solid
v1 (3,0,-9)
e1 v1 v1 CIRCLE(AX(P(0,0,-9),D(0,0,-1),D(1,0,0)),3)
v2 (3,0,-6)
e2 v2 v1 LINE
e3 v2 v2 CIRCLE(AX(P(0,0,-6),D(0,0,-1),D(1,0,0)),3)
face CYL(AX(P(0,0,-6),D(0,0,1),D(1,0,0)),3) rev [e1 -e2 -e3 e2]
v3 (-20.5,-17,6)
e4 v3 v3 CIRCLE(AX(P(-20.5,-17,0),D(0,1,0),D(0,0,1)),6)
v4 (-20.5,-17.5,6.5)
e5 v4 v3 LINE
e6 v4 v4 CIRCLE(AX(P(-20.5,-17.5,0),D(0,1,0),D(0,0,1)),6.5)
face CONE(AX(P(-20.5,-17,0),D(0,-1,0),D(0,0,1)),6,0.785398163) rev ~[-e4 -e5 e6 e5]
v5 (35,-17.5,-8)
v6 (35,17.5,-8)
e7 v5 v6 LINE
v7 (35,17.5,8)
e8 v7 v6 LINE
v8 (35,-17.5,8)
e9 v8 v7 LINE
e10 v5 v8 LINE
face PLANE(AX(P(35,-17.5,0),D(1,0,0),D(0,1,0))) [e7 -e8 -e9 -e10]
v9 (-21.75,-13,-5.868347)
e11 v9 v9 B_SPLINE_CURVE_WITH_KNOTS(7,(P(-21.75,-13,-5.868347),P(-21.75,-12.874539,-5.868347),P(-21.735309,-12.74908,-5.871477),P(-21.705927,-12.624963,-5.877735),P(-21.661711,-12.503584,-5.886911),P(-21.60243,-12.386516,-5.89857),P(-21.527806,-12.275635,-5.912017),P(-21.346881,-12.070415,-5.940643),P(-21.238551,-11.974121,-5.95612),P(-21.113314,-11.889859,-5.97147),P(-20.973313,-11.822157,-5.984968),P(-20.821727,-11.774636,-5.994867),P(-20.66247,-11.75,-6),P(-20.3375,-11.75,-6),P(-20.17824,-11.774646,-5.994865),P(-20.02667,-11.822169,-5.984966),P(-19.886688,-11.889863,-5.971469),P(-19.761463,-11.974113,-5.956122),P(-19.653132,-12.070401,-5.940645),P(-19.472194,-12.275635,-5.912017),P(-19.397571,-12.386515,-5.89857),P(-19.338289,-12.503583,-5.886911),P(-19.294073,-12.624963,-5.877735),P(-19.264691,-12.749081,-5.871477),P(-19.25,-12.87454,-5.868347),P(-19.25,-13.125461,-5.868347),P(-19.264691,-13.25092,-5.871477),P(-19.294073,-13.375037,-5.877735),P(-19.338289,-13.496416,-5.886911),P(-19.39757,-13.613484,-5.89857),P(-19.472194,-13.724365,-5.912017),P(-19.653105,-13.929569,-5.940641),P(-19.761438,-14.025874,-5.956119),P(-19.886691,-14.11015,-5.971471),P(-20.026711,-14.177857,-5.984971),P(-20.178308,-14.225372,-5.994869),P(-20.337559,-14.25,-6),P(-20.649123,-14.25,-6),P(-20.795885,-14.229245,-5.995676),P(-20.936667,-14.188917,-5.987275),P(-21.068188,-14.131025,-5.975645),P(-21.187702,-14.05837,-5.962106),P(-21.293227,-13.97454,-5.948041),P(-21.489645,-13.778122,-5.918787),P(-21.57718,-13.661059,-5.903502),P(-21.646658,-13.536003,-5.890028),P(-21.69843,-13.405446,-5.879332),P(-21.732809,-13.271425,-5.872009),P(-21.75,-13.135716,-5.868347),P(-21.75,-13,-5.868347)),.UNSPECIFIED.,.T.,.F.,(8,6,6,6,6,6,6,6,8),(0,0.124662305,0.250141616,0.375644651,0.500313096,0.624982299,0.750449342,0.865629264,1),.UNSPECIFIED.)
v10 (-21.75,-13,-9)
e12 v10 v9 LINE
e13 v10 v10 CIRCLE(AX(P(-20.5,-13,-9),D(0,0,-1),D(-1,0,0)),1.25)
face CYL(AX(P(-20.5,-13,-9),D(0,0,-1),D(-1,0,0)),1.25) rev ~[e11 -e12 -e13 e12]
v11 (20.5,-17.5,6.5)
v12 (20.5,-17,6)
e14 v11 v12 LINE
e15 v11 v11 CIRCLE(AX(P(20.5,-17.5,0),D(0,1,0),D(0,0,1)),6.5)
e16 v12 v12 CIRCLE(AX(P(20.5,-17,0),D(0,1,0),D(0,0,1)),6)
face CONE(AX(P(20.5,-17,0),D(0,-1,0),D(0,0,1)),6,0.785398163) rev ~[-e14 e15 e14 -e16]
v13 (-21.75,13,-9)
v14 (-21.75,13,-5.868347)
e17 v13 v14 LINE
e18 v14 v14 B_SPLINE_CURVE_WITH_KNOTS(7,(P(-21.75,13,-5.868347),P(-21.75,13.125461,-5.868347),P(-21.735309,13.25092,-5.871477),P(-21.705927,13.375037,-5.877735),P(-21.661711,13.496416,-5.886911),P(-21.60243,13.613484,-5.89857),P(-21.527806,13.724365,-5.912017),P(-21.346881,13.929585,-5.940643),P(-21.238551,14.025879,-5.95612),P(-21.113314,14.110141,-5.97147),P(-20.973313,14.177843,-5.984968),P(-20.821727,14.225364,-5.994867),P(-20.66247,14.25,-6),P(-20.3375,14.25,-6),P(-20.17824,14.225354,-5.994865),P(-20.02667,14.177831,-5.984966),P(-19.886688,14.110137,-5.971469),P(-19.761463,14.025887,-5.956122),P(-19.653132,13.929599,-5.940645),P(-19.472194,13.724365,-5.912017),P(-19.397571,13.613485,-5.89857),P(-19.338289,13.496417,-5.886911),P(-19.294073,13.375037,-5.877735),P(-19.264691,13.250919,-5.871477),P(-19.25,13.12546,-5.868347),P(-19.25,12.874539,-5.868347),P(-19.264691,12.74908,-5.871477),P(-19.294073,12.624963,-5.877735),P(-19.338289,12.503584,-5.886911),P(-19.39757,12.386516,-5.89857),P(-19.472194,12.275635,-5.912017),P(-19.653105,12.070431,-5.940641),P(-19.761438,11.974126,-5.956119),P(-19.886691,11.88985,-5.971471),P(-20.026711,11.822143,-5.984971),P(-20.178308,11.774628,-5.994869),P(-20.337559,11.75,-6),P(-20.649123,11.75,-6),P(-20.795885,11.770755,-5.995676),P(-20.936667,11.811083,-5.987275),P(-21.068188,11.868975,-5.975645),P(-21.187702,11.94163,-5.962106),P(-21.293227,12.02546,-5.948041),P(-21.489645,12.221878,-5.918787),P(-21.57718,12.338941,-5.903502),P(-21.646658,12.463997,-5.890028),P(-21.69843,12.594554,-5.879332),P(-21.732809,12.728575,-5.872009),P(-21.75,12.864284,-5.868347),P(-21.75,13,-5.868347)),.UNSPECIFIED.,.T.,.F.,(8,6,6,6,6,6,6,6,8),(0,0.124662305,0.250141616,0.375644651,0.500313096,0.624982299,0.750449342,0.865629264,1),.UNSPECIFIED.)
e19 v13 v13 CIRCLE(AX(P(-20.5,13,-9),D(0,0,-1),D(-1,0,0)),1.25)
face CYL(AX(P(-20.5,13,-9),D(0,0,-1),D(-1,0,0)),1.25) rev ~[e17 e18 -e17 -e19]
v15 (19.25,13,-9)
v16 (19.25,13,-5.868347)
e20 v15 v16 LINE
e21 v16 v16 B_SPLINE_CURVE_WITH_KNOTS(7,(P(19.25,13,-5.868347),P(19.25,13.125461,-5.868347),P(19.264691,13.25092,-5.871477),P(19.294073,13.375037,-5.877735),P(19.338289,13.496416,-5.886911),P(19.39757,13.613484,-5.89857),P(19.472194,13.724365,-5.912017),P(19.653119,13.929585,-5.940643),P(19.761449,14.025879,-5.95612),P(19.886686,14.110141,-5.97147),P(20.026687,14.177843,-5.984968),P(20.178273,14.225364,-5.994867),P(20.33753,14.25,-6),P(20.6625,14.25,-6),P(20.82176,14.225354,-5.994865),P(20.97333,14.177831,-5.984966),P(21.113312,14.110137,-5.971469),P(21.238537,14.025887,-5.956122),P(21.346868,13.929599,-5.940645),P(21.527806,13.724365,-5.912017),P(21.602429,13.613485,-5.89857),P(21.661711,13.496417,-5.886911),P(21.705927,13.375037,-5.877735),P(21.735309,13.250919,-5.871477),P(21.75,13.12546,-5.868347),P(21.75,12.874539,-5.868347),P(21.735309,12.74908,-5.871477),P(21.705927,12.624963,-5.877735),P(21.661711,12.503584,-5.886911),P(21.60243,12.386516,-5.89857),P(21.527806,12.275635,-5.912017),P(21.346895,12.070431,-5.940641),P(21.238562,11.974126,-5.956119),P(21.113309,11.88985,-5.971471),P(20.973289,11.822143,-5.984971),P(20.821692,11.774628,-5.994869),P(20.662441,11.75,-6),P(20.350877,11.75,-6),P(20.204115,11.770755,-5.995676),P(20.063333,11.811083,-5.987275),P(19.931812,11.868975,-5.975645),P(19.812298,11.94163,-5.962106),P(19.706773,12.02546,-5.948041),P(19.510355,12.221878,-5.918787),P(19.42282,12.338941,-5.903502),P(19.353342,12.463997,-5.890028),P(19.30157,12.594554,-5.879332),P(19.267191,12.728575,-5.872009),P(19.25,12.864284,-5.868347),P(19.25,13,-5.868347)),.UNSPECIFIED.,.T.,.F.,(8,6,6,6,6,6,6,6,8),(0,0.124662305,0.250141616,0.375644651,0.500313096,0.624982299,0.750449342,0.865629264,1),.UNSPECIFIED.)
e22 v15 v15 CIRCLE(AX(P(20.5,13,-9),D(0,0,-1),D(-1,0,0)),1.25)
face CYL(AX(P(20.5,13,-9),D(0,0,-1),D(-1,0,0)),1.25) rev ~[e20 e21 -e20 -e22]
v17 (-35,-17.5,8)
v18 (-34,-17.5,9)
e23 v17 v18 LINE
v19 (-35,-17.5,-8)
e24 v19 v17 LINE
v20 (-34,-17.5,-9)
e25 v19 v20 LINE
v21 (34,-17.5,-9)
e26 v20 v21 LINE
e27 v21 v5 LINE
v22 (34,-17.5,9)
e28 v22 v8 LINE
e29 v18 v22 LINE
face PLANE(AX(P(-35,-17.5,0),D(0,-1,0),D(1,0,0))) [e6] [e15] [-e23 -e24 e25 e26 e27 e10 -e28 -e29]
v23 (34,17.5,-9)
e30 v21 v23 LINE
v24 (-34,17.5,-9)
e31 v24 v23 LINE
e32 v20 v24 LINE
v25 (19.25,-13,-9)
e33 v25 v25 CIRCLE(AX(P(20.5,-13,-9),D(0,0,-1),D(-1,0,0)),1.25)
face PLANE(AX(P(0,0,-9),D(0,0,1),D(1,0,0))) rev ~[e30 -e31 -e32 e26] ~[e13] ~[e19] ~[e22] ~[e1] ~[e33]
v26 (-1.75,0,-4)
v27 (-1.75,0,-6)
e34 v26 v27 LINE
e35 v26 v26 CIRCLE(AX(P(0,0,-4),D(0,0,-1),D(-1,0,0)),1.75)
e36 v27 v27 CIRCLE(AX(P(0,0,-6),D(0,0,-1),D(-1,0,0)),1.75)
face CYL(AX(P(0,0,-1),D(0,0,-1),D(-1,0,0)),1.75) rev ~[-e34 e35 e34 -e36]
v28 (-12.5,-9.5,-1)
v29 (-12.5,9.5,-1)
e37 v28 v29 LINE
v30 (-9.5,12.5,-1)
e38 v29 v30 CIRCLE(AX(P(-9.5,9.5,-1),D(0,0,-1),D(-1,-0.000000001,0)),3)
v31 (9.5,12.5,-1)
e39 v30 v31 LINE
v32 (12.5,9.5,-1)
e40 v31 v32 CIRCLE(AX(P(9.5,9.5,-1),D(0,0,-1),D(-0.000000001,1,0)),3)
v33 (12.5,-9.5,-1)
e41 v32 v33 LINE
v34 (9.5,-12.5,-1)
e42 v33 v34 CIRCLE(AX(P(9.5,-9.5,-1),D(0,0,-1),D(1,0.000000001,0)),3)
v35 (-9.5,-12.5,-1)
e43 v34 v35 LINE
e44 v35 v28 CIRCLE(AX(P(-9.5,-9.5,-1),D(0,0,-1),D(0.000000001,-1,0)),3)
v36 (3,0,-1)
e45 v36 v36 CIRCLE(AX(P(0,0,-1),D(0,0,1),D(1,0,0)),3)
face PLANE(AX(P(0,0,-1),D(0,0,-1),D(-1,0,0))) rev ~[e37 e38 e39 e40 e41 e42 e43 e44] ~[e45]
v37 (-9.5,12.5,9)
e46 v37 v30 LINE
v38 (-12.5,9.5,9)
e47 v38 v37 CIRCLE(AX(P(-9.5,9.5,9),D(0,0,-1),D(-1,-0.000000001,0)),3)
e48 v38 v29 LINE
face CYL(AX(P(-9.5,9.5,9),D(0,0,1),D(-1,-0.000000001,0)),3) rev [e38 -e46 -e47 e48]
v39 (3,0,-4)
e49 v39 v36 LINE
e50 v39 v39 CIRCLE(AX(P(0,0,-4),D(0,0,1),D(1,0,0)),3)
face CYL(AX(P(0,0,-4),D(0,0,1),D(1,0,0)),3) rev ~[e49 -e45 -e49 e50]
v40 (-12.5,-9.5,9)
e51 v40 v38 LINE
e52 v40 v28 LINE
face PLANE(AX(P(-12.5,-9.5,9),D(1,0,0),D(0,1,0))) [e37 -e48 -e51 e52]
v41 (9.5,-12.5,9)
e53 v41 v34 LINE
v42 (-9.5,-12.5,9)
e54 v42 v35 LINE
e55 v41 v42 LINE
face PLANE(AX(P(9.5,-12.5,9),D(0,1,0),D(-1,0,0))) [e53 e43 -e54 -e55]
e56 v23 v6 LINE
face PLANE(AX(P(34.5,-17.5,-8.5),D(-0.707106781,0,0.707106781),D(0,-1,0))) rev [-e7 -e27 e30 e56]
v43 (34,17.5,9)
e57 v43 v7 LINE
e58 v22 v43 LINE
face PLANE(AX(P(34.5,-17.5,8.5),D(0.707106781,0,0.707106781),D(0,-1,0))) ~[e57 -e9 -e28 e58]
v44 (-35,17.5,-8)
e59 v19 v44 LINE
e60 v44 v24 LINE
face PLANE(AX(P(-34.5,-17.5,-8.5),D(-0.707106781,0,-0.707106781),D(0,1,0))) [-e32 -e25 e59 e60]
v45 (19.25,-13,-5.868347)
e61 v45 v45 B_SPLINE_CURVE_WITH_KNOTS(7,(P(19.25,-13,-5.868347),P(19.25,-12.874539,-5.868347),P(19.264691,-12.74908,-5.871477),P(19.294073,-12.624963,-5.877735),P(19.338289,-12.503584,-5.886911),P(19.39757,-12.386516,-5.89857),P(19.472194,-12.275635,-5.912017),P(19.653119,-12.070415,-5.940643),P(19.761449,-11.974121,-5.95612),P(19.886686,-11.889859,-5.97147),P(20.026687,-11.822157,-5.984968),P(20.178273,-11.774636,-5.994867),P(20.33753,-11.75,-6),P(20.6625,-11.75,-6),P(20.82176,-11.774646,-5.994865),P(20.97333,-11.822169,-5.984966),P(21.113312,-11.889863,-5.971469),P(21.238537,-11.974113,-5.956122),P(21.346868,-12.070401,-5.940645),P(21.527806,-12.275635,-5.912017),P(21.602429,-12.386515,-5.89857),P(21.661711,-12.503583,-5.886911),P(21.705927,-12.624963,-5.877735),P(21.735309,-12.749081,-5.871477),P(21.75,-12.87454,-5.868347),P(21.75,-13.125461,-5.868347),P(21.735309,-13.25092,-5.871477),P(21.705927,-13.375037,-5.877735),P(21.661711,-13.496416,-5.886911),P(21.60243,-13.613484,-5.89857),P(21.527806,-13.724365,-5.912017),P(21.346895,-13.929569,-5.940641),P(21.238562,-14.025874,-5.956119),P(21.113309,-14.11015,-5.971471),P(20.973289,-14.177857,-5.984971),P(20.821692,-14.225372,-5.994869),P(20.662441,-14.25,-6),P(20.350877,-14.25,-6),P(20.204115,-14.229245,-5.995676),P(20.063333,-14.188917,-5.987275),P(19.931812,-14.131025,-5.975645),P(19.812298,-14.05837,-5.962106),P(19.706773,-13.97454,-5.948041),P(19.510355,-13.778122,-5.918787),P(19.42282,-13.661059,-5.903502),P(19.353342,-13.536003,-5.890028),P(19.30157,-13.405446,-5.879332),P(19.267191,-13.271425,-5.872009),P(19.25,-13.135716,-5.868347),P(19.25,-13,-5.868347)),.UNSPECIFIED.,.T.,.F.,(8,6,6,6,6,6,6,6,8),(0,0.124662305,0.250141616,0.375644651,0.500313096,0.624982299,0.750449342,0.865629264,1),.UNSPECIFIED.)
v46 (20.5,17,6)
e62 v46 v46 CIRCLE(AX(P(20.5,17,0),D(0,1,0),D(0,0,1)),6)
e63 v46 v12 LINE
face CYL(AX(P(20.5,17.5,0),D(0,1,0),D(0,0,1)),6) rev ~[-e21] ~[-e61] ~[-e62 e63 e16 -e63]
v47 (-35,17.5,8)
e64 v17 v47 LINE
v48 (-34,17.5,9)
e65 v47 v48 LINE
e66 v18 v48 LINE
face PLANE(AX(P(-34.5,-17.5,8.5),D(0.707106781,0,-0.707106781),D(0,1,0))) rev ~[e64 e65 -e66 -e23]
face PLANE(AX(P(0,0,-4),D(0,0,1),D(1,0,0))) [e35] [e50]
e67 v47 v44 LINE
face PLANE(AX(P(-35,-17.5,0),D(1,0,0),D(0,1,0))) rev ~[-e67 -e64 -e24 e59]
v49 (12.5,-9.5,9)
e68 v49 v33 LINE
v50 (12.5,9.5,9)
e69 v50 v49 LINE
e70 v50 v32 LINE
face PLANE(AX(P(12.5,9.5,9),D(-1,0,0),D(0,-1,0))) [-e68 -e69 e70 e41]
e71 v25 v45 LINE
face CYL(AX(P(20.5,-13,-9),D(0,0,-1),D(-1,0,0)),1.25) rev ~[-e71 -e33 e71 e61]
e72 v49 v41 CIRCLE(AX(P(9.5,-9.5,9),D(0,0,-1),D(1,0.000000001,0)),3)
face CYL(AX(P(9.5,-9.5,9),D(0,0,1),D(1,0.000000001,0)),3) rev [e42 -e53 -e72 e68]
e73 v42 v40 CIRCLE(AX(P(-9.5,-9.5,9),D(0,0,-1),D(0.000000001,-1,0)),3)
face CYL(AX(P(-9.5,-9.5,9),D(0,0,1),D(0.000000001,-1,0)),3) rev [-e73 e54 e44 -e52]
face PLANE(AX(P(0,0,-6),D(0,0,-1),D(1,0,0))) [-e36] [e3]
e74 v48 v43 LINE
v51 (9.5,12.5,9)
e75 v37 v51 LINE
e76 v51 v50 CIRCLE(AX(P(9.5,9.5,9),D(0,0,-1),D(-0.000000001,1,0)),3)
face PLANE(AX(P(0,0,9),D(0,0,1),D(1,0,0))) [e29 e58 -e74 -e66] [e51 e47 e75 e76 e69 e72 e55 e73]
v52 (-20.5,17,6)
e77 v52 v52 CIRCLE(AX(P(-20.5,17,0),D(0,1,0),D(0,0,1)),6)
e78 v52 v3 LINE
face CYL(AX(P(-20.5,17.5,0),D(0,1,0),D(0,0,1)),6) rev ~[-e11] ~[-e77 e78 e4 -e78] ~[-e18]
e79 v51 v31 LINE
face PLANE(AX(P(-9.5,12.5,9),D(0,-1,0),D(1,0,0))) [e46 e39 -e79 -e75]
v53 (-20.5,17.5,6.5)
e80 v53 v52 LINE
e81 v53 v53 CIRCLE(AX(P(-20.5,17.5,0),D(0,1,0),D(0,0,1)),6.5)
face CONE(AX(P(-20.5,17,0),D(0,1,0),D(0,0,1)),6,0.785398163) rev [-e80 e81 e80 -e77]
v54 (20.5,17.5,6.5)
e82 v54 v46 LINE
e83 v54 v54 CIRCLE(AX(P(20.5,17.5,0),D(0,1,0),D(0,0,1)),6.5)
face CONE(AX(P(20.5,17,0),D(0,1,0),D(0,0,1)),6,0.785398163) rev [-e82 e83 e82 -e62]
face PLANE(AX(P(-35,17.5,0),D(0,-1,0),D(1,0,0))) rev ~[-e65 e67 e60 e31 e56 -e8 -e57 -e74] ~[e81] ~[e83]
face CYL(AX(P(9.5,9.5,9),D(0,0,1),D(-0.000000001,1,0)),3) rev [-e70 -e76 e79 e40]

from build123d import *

# Parameters (mm, degrees)
SKETCH1_W                               = 70
SKETCH1_H                               = 35
BOSS_EXTRUDE1_DEPTH                     = 9
CUT_EXTRUDE1_DEPTH                      = 10
SKETCH3_R                               = 6
CUT_EXTRUDE2_DEPTH                      = 51.309044912
M3_TAPPED_HOLE1_REACH                   = 45.073
M3_TAPPED_HOLE1_BORE_R                  = 1.25
CBORE_FOR_M3_HEX_HEAD_BOLT1_D           = 3.5
CBORE_FOR_M3_HEX_HEAD_BOLT1_CBORE_D     = 6
CBORE_FOR_M3_HEX_HEAD_BOLT1_CBORE_DEPTH = 3
CUT_EXTRUDE3_START                      = -3
SKETCH9_R                               = 3
CUT_EXTRUDE3_DEPTH                      = 3
CHAMFER1_SIZE                           = 1
CHAMFER2_SIZE                           = 0.5


with BuildPart() as part:
    # Sketch1 → Boss-Extrude1 (new, symmetric)
    with BuildSketch(Plane.XY):
        Rectangle(SKETCH1_W, SKETCH1_H)
    extrude(amount=BOSS_EXTRUDE1_DEPTH, both=True)

    # Sketch2 → Cut-Extrude1 (cut)
    with BuildSketch(Plane.XY.offset(9)):
        with BuildLine():
            Line((-9.5, 12.5), (9.5, 12.5))
            ThreePointArc((9.5, 12.5), (11.621320344, 11.621320344), (12.5, 9.5))
            Line((12.5, 9.5), (12.5, -9.5))
            ThreePointArc((12.5, -9.5), (11.621320344, -11.621320344), (9.5, -12.5))
            Line((9.5, -12.5), (-9.5, -12.5))
            ThreePointArc((-9.5, -12.5), (-11.621320344, -11.621320344), (-12.5, -9.5))
            Line((-12.5, -9.5), (-12.5, 9.5))
            ThreePointArc((-12.5, 9.5), (-11.621320344, 11.621320344), (-9.5, 12.5))
        make_face()
    extrude(amount=-CUT_EXTRUDE1_DEPTH, mode=Mode.SUBTRACT)

    # Sketch3 → Cut-Extrude2 (cut, through all)
    with BuildSketch(Plane(origin=(0, 17.5, 0), x_dir=(1, 0, 0), z_dir=(0, 1, 0))):
        with Locations(Location((-20.5, 0, 0), (0, 0, 270))):
            Circle(SKETCH3_R)
        with Locations(Location((20.5, 0, 0), (0, 0, 270))):
            Circle(SKETCH3_R)
    extrude(amount=-CUT_EXTRUDE2_DEPTH, mode=Mode.SUBTRACT)

    # M3 Tapped Hole1 bore → M3 Tapped Hole1 (cut, up to next)
    with BuildSketch(Plane(origin=(0, 0, -9), x_dir=(-1, 0, 0), z_dir=(0, 0, -1)), mode=Mode.PRIVATE) as m3_tapped_hole1_sk1:
        with Locations((-20.5, 13)):
            Circle(M3_TAPPED_HOLE1_BORE_R)
    m3_tapped_hole1_tool1 = extrude(m3_tapped_hole1_sk1.sketch, amount=-M3_TAPPED_HOLE1_REACH, mode=Mode.PRIVATE) & part.part
    # M3 Tapped Hole1 bore → M3 Tapped Hole1 (cut, up to next)
    with BuildSketch(Plane(origin=(0, 0, -9), x_dir=(-1, 0, 0), z_dir=(0, 0, -1)), mode=Mode.PRIVATE) as m3_tapped_hole1_sk2:
        with Locations((-20.5, -13)):
            Circle(M3_TAPPED_HOLE1_BORE_R)
    m3_tapped_hole1_tool2 = extrude(m3_tapped_hole1_sk2.sketch, amount=-M3_TAPPED_HOLE1_REACH, mode=Mode.PRIVATE) & part.part
    # M3 Tapped Hole1 bore → M3 Tapped Hole1 (cut, up to next)
    with BuildSketch(Plane(origin=(0, 0, -9), x_dir=(-1, 0, 0), z_dir=(0, 0, -1)), mode=Mode.PRIVATE) as m3_tapped_hole1_sk3:
        with Locations((20.5, -13)):
            Circle(M3_TAPPED_HOLE1_BORE_R)
    m3_tapped_hole1_tool3 = extrude(m3_tapped_hole1_sk3.sketch, amount=-M3_TAPPED_HOLE1_REACH, mode=Mode.PRIVATE) & part.part
    # M3 Tapped Hole1 bore → M3 Tapped Hole1 (cut, up to next)
    with BuildSketch(Plane(origin=(0, 0, -9), x_dir=(-1, 0, 0), z_dir=(0, 0, -1)), mode=Mode.PRIVATE) as m3_tapped_hole1_sk4:
        with Locations((20.5, 13)):
            Circle(M3_TAPPED_HOLE1_BORE_R)
    m3_tapped_hole1_tool4 = extrude(m3_tapped_hole1_sk4.sketch, amount=-M3_TAPPED_HOLE1_REACH, mode=Mode.PRIVATE) & part.part
    add(m3_tapped_hole1_tool1.solids().sort_by_distance((20.5, 13, -9))[0], mode=Mode.SUBTRACT)
    add(m3_tapped_hole1_tool2.solids().sort_by_distance((20.5, -13, -9))[0], mode=Mode.SUBTRACT)
    add(m3_tapped_hole1_tool3.solids().sort_by_distance((-20.5, -13, -9))[0], mode=Mode.SUBTRACT)
    add(m3_tapped_hole1_tool4.solids().sort_by_distance((-20.5, 13, -9))[0], mode=Mode.SUBTRACT)

    # CBORE for M3 Hex Head Bolt1 (through all)
    with Locations(Plane(origin=(-21.223251094, -7.58728159, -1), x_dir=(1, 0, 0), z_dir=(0, 0, 1))):
        with Locations((21.223251094, 7.58728159)):
            CounterBoreHole(CBORE_FOR_M3_HEX_HEAD_BOLT1_D / 2, CBORE_FOR_M3_HEX_HEAD_BOLT1_CBORE_D / 2, CBORE_FOR_M3_HEX_HEAD_BOLT1_CBORE_DEPTH)

    # Sketch9 → Cut-Extrude3 (cut)
    with BuildSketch(Plane(origin=(0, 0, -9), x_dir=(-1, 0, 0), z_dir=(0, 0, -1)).offset(CUT_EXTRUDE3_START)):
        with Locations(Location((0, 0, 0), (0, 0, 180))):
            Circle(SKETCH9_R)
    extrude(amount=CUT_EXTRUDE3_DEPTH, mode=Mode.SUBTRACT)

    # Chamfer1
    chamfer1_edges = [part.edges().sort_by_distance(p)[0] for p in [
        (-35, 0, 9),
        (35, 0, 9),
        (-35, 0, -9),
        (35, 0, -9),
    ]]
    chamfer(chamfer1_edges, length=CHAMFER1_SIZE)

    # Chamfer2
    chamfer2_edges = [part.edges().sort_by_distance(p)[0] for p in [
        (-20.5, -17.5, -6),
        (-20.5, 17.5, -6),
        (20.5, -17.5, -6),
        (20.5, 17.5, -6),
    ]]
    chamfer(chamfer2_edges, length=CHAMFER2_SIZE)


solid = part.part
